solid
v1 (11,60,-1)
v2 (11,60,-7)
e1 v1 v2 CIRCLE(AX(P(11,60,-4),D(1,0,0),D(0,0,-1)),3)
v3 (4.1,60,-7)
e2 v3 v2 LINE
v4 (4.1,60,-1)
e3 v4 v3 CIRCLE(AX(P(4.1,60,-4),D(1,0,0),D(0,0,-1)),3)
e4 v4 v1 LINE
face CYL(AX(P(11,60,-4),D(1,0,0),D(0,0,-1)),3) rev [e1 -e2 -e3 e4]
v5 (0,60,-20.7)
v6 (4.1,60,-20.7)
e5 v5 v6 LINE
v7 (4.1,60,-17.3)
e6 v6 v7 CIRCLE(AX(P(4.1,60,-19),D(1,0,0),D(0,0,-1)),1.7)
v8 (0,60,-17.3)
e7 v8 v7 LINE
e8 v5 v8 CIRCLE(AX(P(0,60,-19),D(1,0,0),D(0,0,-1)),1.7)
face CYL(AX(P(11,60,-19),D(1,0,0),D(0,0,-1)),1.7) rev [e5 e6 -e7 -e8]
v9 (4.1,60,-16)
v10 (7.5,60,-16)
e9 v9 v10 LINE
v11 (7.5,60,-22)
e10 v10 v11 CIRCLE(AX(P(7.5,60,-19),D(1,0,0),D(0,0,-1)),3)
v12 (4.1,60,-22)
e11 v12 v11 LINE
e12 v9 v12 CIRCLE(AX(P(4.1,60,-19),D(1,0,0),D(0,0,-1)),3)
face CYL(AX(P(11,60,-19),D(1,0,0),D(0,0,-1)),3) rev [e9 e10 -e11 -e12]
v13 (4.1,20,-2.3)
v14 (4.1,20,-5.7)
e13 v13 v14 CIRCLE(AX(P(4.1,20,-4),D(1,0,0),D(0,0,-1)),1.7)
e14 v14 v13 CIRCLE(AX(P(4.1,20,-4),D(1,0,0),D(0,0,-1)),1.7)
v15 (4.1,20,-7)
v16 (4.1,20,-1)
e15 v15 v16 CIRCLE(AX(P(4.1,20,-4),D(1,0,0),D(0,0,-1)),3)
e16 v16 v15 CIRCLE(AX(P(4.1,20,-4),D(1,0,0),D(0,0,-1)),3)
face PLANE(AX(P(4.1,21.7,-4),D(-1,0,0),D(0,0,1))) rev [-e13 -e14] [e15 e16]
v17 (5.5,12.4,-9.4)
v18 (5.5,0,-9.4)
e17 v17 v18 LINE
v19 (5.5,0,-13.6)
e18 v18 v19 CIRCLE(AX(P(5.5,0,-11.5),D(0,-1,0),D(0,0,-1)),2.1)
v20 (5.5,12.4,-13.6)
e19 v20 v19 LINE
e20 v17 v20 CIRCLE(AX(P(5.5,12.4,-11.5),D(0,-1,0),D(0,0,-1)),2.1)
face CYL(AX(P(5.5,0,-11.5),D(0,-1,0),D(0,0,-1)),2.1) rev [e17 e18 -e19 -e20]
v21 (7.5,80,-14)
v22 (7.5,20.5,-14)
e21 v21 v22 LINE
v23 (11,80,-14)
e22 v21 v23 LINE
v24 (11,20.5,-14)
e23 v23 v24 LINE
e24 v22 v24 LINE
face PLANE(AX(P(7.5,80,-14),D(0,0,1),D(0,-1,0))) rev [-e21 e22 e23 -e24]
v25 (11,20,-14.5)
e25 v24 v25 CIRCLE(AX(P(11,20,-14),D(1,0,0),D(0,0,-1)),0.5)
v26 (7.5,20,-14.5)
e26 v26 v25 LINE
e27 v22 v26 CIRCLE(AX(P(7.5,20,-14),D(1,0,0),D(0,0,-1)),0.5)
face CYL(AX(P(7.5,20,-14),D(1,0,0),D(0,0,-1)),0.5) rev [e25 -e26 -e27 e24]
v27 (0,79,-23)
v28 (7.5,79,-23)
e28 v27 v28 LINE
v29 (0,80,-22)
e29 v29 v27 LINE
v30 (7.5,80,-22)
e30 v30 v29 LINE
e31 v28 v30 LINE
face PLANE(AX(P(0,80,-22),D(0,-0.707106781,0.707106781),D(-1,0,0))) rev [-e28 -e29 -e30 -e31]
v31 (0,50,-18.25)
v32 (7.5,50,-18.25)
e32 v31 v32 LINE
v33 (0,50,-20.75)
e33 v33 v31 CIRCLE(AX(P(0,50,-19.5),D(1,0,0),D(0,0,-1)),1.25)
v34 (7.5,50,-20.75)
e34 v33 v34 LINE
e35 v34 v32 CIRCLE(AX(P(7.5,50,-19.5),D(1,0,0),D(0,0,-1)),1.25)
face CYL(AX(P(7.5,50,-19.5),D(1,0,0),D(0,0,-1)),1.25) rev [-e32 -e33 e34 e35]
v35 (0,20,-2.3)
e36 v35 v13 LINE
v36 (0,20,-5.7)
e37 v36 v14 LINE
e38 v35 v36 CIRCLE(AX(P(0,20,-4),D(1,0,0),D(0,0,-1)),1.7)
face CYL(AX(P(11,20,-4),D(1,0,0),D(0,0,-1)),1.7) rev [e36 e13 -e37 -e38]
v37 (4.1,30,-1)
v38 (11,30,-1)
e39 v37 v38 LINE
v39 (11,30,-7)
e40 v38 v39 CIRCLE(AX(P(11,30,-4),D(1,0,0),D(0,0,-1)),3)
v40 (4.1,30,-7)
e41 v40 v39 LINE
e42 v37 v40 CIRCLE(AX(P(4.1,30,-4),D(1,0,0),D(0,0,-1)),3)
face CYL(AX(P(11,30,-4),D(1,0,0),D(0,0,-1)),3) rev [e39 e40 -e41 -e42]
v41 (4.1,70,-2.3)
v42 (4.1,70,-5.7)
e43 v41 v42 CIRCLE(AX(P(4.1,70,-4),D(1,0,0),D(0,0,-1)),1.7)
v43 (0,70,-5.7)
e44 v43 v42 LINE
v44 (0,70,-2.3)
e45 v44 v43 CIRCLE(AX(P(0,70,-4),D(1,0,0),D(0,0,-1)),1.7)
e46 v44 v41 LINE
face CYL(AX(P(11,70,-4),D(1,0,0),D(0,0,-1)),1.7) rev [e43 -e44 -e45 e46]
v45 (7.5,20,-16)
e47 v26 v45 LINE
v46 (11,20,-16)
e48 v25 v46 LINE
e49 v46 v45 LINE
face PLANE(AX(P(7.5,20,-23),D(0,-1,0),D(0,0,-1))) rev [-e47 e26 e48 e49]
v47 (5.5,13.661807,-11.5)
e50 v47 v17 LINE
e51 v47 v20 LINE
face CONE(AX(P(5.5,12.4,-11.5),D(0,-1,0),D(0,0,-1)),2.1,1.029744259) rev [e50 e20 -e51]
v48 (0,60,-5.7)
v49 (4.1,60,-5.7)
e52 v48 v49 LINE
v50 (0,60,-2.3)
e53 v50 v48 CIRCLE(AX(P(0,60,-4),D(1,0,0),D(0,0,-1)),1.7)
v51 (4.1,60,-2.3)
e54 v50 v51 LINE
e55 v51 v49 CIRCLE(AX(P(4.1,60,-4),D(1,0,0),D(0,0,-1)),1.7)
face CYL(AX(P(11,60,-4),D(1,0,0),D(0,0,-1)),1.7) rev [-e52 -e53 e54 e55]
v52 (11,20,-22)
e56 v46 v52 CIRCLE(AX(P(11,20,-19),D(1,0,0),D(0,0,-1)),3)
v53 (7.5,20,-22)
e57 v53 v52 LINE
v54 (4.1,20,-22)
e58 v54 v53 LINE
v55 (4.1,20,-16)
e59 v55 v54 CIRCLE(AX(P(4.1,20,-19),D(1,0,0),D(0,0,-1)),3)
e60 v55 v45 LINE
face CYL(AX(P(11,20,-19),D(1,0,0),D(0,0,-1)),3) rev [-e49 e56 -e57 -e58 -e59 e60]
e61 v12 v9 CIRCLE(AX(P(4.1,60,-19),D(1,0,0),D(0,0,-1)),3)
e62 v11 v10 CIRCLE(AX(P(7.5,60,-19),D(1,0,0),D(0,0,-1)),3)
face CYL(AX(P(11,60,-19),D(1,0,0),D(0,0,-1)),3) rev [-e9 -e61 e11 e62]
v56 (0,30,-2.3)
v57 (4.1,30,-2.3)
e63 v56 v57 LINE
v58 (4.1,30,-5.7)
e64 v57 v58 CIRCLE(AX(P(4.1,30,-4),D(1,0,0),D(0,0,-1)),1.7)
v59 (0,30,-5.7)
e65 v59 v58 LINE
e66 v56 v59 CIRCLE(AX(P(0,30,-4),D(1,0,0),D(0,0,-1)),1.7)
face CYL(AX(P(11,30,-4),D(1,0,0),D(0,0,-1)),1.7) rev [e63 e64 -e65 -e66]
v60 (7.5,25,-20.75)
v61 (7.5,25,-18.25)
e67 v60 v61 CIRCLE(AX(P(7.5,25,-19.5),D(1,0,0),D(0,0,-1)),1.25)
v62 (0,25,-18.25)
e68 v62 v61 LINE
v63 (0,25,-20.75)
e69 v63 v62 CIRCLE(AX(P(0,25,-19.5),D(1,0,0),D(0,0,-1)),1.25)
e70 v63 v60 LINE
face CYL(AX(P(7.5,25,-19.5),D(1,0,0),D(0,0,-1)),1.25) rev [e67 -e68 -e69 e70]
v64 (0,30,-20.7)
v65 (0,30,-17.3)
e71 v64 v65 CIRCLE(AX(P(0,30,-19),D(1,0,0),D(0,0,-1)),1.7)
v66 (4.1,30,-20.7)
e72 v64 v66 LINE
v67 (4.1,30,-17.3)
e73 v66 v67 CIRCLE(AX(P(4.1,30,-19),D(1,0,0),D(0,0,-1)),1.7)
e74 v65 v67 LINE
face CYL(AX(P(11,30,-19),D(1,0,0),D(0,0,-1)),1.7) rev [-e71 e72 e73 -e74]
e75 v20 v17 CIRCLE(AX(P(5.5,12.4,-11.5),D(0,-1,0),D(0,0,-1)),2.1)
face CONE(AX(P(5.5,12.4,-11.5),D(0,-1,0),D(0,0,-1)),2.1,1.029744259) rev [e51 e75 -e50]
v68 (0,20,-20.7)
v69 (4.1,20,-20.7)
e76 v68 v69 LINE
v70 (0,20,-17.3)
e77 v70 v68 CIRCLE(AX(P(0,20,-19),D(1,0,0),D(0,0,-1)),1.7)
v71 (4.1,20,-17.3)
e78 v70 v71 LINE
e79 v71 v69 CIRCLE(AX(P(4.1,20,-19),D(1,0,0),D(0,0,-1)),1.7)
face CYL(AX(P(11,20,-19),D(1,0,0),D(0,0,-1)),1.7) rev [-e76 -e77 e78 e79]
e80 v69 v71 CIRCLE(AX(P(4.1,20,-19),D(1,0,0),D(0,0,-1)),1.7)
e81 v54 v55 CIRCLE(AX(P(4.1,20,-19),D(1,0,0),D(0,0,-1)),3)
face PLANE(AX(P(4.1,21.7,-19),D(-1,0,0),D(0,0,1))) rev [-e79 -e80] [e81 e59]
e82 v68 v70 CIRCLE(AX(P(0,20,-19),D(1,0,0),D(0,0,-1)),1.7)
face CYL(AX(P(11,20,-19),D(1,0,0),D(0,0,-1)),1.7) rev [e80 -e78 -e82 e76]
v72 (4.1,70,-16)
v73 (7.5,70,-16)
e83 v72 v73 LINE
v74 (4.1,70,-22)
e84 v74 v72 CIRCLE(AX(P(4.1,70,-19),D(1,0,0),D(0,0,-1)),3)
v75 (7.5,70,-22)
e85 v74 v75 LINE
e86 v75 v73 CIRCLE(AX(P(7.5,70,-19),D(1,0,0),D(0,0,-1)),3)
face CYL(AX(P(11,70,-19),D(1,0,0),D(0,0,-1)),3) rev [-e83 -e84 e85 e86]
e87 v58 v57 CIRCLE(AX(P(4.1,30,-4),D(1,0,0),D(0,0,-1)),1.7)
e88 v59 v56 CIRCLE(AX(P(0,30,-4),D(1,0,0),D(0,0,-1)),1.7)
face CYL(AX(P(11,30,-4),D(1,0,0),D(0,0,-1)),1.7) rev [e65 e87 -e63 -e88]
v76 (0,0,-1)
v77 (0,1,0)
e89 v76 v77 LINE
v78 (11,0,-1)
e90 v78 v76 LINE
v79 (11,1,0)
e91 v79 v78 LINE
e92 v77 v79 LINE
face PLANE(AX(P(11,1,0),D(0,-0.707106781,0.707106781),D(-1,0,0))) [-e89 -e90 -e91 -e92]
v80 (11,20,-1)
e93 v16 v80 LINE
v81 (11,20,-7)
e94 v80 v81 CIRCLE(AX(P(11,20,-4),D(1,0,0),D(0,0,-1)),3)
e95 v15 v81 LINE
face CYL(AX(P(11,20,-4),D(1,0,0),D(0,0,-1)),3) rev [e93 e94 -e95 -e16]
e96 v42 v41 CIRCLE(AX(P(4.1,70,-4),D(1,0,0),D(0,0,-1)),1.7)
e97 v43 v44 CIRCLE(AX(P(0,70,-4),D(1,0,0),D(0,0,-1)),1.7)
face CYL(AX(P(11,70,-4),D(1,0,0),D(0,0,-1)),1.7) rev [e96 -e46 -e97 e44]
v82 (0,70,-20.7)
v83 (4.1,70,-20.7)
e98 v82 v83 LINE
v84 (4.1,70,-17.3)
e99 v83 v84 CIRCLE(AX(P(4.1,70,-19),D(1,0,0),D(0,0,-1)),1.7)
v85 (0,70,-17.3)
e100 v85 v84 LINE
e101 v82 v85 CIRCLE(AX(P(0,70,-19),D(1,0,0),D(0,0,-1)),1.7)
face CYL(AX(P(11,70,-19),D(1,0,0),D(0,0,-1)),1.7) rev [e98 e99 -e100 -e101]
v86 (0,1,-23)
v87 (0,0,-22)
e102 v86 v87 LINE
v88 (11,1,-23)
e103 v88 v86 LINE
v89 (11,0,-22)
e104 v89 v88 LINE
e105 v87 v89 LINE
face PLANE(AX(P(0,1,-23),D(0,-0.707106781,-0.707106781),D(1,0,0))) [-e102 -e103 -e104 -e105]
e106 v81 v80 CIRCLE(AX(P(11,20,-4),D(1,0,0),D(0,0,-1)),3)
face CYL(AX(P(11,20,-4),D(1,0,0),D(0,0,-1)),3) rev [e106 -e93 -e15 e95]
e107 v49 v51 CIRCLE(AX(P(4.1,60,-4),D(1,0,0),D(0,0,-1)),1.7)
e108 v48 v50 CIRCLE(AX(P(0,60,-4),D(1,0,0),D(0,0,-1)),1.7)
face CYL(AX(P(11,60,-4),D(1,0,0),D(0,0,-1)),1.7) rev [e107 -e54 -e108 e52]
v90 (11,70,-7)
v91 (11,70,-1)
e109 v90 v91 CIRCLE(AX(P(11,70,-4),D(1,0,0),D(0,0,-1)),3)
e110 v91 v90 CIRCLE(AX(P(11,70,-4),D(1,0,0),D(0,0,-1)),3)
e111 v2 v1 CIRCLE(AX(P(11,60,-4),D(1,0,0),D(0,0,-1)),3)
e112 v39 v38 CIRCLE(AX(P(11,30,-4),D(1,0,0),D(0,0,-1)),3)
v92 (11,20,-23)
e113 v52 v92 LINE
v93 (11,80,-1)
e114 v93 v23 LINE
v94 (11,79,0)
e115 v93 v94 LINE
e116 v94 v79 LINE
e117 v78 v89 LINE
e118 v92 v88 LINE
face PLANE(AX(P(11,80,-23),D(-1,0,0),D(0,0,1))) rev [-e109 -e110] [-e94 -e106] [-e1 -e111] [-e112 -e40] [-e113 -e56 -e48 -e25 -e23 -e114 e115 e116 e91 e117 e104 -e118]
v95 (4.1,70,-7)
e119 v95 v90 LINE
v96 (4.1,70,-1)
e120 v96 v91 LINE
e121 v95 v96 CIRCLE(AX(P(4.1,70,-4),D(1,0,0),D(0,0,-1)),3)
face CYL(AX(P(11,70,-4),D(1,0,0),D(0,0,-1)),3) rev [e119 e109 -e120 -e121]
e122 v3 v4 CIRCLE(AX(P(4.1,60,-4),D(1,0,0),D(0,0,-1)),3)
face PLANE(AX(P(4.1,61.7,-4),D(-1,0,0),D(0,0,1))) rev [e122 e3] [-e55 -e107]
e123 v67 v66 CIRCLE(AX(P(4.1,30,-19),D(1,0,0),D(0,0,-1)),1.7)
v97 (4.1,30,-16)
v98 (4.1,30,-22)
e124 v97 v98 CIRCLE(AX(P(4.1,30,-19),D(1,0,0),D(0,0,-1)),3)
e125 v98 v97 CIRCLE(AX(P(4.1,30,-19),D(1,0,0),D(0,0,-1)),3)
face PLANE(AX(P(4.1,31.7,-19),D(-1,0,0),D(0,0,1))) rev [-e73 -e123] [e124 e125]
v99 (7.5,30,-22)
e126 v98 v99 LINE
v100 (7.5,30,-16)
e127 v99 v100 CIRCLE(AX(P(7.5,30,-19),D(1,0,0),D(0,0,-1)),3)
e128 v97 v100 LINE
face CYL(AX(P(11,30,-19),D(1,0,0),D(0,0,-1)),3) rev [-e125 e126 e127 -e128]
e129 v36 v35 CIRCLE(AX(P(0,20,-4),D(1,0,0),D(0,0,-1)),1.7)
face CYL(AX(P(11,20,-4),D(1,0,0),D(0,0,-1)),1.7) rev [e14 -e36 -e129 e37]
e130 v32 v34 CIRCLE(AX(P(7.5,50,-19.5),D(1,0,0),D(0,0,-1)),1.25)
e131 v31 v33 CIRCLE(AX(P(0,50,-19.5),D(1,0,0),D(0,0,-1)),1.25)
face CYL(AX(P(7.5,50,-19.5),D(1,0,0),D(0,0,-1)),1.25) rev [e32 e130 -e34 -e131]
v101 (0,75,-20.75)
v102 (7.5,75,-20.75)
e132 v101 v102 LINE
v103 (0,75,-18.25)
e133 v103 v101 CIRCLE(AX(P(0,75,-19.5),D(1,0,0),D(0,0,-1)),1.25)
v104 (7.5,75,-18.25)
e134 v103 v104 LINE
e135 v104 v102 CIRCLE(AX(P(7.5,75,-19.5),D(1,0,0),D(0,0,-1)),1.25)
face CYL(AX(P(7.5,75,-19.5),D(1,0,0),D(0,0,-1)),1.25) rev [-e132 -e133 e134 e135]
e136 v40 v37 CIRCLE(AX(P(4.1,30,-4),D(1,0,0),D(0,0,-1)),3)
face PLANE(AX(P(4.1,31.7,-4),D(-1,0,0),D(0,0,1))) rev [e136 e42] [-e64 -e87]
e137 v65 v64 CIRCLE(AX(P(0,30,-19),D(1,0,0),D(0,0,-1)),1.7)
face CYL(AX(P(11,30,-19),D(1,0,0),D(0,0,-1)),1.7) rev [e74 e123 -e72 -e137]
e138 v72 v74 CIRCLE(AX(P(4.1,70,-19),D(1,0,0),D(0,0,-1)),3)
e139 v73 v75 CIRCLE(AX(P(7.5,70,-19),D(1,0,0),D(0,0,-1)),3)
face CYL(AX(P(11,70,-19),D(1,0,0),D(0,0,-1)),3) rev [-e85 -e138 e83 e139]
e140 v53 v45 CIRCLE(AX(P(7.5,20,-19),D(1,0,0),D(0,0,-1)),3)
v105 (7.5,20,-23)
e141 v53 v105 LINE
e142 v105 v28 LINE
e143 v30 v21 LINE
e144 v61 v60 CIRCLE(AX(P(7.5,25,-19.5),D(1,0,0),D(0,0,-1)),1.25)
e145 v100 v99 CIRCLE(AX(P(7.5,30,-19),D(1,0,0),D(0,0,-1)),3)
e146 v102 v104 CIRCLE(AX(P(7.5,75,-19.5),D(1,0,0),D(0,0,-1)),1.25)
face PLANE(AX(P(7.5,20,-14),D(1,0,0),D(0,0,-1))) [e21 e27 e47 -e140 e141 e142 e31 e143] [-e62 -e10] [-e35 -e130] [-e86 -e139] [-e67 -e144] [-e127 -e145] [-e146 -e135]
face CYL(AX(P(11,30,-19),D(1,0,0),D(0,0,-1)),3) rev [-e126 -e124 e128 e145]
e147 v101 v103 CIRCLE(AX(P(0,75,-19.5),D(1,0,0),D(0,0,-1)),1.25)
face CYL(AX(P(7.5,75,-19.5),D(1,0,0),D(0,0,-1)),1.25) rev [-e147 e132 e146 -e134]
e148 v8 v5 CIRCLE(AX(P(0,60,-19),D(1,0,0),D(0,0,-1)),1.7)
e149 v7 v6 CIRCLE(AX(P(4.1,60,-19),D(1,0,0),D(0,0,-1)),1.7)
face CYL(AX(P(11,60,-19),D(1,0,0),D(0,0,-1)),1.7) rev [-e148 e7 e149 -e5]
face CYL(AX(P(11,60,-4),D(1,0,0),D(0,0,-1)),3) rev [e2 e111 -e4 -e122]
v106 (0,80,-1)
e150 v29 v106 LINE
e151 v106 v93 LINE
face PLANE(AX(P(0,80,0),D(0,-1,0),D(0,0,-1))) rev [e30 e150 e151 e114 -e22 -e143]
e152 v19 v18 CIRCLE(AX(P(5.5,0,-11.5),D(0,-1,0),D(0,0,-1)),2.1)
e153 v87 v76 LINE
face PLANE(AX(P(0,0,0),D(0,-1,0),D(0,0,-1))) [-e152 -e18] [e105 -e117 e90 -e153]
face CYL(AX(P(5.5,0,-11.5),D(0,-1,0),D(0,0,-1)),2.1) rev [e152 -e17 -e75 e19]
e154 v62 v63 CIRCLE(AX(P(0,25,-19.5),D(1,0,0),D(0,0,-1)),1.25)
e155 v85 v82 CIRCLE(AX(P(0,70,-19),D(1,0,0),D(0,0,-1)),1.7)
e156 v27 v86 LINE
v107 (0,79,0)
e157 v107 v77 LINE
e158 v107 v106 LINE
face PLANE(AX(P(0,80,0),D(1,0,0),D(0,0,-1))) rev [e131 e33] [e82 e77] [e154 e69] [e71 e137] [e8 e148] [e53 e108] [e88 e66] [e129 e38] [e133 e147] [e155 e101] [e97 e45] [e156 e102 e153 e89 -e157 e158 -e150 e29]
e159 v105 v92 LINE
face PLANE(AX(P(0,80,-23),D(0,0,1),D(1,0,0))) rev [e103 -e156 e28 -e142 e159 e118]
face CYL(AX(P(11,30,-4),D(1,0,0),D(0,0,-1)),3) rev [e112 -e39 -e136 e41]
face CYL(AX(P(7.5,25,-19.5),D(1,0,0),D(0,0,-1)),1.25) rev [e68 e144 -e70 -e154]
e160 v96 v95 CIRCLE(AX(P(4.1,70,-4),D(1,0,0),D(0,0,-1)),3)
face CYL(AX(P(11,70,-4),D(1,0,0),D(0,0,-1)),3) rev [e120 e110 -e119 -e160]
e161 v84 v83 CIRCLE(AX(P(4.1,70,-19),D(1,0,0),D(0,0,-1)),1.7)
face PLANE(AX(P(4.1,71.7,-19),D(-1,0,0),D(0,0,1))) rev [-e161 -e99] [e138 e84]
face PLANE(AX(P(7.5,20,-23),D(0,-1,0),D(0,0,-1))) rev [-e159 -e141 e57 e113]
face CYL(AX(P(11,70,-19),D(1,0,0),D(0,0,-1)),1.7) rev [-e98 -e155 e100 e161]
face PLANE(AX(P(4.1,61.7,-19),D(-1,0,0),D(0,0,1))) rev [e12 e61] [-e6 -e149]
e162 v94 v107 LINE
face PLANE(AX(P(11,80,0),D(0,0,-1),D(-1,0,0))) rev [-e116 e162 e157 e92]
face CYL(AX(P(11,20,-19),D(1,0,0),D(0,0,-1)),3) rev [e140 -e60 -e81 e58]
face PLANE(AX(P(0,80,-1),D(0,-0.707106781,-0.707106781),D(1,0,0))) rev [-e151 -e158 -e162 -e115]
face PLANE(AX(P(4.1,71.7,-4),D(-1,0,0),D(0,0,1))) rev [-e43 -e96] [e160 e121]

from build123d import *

# Parameters (mm, degrees)
SKETCH_1_W                = 11
SKETCH_1_H                = 23
EXTRUDE_1_DEPTH           = 80
CUT_EXTRUDE_1_DEPTH       = 3.5
HOLE_WIZARD_2_D           = 3.4
HOLE_WIZARD_2_CBORE_D     = 6
HOLE_WIZARD_2_CBORE_DEPTH = 6.9
HOLE_WIZARD_M5_1_D        = 4.2
HOLE_WIZARD_M5_1_DEPTH    = 12.4
HOLE_WIZARD_M5_1_TIP      = 1.2618073
HOLE_WIZARD_M3_1_D        = 2.5
CHAMFER_1_SIZE            = 1


with BuildPart() as part:
    # 草图1 → 凸台-拉伸1 (new body)
    with BuildSketch(Plane(origin=(0, 0, 0), x_dir=(1, 0, 0), z_dir=(0, 1, 0))):
        with Locations((5.5, 11.5)):
            Rectangle(SKETCH_1_W, SKETCH_1_H)
    extrude(amount=EXTRUDE_1_DEPTH)

    # 草图2 → 切除-拉伸1 (cut)
    with BuildSketch(Plane(origin=(11, 0, 0), x_dir=(0, 0, -1), z_dir=(1, 0, 0))):
        with BuildLine():
            Line((23, 80), (14, 80))
            Line((14, 80), (14, 20.5))
            ThreePointArc((14, 20.5), (13.646446609, 19.646446609), (14.5, 20))
            Line((14.5, 20), (23, 20))
            Line((23, 20), (23, 80))
        make_face()
    extrude(amount=-CUT_EXTRUDE_1_DEPTH, mode=Mode.SUBTRACT)

    # 打孔尺寸(%根据)内六角圆柱头螺钉的类型2 (through all)
    with Locations(Plane(origin=(11, 0, 0), x_dir=(0, 0, -1), z_dir=(1, 0, 0))):
        with Locations((4, 20), (4, 30), (19, 30), (19, 20), (4, 60), (4, 70), (19, 60), (19, 70)):
            CounterBoreHole(HOLE_WIZARD_2_D / 2, HOLE_WIZARD_2_CBORE_D / 2, HOLE_WIZARD_2_CBORE_DEPTH)

    # M5 螺纹孔1
    with Locations(Plane(origin=(0, 0, 0), x_dir=(-1, 0, 0), z_dir=(0, -1, 0))):
        with Locations((-5.5, 11.5)):
            Hole(HOLE_WIZARD_M5_1_D / 2, depth=HOLE_WIZARD_M5_1_DEPTH)
            with Locations((0, 0, -(HOLE_WIZARD_M5_1_DEPTH + HOLE_WIZARD_M5_1_TIP / 2))):  # 118° drill point
                Cone(0, HOLE_WIZARD_M5_1_D / 2, HOLE_WIZARD_M5_1_TIP, mode=Mode.SUBTRACT)

    # M3 螺纹孔1 (through all)
    with Locations(Plane(origin=(7.5, 0, 0), x_dir=(0, 0, -1), z_dir=(1, 0, 0))):
        with Locations((19.5, 25), (19.5, 50), (19.5, 75)):
            Hole(HOLE_WIZARD_M3_1_D / 2)

    # 倒角1
    chamfer_1_edges = [part.edges().sort_by_distance(p)[0] for p in [
        (3.75, 80, -23),
        (5.5, 80, 0),
        (5.5, 0, -23),
        (5.5, 0, 0),
    ]]
    chamfer(chamfer_1_edges, length=CHAMFER_1_SIZE)


solid = part.part
